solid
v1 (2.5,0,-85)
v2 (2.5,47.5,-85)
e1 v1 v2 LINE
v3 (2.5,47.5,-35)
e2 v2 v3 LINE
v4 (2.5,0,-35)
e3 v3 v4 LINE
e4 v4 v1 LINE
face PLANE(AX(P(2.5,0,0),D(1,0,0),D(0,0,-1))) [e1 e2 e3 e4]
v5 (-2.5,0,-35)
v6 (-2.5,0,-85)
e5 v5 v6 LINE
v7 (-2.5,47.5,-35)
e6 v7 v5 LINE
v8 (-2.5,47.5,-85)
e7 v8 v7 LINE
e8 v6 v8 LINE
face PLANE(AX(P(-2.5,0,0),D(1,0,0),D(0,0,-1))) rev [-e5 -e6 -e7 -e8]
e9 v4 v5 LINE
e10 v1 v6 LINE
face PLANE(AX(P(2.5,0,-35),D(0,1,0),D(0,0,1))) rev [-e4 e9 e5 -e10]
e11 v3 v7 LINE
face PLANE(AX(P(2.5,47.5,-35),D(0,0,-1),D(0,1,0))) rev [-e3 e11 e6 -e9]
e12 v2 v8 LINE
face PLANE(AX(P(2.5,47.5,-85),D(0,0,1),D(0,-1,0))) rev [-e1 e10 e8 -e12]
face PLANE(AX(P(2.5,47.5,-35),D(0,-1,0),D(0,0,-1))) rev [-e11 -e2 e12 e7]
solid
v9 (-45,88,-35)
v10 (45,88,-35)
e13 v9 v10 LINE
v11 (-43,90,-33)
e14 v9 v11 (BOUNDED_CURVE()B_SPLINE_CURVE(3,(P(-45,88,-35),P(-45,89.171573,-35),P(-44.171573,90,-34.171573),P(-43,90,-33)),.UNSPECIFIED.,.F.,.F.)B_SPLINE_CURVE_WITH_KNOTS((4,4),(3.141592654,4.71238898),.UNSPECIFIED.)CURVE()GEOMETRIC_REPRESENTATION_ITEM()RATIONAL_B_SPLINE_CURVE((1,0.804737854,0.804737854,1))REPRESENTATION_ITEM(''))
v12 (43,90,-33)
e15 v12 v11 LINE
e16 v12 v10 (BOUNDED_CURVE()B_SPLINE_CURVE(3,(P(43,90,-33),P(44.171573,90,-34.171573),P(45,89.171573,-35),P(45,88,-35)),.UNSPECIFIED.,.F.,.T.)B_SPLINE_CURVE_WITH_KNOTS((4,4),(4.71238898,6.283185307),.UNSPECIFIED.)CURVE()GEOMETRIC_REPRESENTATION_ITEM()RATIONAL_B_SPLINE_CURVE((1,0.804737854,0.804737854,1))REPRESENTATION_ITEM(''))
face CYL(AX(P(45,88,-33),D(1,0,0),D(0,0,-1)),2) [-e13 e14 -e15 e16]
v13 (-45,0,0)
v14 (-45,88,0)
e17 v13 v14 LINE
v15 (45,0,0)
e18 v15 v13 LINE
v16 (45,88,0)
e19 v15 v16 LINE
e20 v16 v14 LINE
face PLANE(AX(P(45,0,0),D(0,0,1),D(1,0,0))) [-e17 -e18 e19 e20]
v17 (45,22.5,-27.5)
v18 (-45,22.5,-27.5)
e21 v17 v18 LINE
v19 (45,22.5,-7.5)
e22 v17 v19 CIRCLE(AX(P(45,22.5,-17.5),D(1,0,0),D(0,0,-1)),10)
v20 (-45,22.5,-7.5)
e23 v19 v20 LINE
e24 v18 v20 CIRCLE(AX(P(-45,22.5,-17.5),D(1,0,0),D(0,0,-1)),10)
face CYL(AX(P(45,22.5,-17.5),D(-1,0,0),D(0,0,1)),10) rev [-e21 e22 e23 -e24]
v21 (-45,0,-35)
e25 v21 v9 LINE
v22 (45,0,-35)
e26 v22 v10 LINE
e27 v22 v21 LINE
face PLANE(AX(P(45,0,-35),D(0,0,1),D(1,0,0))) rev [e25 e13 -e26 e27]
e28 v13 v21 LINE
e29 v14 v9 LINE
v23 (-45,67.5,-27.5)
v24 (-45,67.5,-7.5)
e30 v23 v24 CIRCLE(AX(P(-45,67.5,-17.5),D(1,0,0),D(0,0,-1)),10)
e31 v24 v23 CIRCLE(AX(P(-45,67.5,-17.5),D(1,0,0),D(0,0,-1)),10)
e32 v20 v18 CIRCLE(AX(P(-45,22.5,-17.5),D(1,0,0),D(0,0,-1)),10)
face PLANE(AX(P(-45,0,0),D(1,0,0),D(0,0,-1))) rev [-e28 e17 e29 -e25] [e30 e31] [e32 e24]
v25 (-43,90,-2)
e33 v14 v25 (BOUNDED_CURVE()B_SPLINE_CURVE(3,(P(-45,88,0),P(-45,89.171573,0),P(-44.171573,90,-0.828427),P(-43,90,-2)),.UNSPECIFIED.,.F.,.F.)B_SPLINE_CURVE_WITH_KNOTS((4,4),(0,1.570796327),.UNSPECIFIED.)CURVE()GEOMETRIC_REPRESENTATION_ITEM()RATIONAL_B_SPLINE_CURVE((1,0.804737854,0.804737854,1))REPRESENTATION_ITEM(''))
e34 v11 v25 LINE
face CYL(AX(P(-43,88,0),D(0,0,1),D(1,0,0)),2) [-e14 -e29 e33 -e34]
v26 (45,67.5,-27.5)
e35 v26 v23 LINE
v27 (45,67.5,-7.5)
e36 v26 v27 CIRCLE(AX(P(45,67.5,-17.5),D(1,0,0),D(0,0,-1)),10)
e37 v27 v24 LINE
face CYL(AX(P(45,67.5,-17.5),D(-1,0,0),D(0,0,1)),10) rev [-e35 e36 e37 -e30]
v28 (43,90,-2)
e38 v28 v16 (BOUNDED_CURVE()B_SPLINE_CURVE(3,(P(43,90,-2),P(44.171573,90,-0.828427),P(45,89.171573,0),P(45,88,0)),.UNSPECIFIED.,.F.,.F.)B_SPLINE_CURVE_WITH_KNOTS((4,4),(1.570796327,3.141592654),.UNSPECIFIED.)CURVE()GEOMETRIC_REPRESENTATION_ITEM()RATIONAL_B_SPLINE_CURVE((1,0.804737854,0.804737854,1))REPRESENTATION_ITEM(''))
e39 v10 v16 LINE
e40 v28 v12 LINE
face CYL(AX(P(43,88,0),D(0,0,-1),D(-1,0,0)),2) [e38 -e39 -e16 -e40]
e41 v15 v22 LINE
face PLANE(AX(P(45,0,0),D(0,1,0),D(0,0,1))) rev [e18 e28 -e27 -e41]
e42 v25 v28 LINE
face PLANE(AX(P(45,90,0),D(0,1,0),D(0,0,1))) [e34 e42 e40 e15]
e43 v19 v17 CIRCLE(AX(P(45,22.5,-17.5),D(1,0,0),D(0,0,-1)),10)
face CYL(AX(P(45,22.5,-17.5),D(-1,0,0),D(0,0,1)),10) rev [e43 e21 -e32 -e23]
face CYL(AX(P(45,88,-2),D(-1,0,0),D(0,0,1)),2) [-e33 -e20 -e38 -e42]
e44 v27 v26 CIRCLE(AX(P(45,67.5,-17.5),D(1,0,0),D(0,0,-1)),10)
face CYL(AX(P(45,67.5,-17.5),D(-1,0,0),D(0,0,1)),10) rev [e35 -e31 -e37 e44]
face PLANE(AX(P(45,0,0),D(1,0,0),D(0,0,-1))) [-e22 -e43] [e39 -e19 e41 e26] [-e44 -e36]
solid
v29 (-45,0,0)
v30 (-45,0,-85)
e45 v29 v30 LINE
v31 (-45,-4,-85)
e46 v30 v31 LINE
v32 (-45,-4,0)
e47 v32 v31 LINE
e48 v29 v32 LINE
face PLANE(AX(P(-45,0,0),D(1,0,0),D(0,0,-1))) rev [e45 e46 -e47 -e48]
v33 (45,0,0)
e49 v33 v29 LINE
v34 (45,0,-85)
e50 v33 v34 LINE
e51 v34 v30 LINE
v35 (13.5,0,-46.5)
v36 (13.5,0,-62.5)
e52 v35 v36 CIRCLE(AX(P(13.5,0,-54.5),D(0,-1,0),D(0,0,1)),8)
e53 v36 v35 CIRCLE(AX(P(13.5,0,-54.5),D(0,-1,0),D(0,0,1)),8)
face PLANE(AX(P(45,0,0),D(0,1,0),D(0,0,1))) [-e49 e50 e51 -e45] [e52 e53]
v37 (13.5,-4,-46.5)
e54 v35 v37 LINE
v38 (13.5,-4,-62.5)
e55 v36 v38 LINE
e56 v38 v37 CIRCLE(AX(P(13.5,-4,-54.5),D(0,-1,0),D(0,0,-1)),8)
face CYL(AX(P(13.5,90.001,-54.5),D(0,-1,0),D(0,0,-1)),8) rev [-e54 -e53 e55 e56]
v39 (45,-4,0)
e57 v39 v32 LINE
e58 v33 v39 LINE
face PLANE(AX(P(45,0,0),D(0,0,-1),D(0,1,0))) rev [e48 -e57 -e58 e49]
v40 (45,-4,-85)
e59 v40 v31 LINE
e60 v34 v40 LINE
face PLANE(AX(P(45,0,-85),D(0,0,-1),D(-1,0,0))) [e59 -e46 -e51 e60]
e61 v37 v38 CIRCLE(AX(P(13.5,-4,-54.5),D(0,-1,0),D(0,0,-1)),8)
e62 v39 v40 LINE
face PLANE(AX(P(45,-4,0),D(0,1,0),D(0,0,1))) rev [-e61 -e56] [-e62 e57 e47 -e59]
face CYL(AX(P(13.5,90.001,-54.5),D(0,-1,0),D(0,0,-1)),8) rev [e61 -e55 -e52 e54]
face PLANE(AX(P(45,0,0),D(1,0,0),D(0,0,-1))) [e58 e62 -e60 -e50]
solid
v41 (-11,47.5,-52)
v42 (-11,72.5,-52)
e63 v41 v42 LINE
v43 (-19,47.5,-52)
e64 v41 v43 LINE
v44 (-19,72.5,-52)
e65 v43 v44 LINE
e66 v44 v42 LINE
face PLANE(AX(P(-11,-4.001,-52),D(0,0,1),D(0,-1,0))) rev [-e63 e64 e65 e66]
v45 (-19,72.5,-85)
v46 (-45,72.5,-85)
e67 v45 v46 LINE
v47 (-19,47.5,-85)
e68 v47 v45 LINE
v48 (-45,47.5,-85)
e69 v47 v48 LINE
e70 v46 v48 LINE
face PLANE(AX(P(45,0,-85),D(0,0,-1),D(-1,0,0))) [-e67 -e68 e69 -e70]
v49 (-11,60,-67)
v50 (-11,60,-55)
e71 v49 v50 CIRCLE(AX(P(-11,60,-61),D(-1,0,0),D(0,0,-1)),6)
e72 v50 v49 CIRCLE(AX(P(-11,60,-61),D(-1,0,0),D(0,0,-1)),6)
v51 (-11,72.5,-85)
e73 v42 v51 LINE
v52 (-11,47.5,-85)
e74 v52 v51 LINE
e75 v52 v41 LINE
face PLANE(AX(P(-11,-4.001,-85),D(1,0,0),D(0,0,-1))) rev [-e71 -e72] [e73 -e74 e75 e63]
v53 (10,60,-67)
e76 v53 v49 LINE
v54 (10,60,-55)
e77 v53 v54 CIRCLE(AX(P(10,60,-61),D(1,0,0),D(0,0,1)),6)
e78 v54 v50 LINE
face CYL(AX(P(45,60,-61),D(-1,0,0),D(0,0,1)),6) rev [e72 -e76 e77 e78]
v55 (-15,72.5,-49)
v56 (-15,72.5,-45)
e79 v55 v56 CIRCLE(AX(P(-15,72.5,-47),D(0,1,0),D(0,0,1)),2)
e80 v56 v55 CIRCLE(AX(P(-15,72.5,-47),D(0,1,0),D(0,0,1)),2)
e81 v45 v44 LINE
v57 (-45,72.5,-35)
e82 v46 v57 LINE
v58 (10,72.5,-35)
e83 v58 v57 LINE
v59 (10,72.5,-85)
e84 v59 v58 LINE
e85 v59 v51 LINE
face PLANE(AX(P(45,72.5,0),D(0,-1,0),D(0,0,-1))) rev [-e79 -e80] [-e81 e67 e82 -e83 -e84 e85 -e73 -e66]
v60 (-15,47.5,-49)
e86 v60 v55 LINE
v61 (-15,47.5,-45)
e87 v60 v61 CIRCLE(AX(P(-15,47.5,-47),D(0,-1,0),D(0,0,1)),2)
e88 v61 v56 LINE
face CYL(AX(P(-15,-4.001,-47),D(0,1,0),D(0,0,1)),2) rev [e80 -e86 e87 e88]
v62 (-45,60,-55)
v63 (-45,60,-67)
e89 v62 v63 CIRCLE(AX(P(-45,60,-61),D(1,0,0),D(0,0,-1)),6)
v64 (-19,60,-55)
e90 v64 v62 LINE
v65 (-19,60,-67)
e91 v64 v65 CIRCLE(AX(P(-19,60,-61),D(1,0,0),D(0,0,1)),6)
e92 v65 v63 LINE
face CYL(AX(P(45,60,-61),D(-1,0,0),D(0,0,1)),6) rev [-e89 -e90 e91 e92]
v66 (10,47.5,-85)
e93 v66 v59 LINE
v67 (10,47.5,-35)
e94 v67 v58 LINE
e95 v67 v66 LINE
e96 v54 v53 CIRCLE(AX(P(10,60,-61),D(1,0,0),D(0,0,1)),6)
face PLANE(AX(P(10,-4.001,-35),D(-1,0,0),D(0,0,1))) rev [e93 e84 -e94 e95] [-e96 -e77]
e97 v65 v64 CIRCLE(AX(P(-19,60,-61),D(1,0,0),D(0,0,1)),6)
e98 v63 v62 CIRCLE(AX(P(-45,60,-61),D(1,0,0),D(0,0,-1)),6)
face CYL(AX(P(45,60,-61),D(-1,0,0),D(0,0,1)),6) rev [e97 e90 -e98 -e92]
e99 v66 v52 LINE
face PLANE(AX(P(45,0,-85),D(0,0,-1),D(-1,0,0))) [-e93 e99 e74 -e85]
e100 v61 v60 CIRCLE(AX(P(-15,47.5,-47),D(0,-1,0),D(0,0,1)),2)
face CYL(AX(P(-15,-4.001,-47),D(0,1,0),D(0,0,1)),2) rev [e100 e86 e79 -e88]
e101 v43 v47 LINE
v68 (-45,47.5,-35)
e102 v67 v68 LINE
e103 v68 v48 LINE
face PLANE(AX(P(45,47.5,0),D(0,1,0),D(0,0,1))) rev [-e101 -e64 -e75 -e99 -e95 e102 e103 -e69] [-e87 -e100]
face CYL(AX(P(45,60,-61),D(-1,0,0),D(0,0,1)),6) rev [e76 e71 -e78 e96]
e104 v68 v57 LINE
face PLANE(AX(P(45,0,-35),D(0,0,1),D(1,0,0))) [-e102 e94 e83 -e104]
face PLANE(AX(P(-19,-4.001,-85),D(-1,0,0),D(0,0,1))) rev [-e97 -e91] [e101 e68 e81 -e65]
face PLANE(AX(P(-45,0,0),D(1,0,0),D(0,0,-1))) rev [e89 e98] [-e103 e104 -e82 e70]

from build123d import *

# Parameters (mm, degrees)
SKETCH1_R           = 10
BOSS_EXTRUDE1_DEPTH = 45
SKETCH1_3_W         = 50
SKETCH1_3_H         = 25
SKETCH1_3_R         = 6
BOSS_EXTRUDE3_DEPTH = 45
BOSS_EXTRUDE4_DEPTH = 45
SKETCH2_R           = 2
SKETCH2_W           = 35
SKETCH2_H           = 50
SKETCH2_W_2         = 8
SKETCH2_H_2         = 33
CUT_EXTRUDE1_DEPTH  = 25
SKETCH3_W           = 50
SKETCH3_H           = 47.5
BOSS_EXTRUDE2_DEPTH = 2.5
FILLET1_R           = 2
SKETCH4_R           = 8
CUT_EXTRUDE2_DEPTH  = 4


with BuildPart() as part:
    # Sketch1 → Boss-Extrude1 (new, symmetric)
    with BuildSketch(Plane(origin=(0, 0, 0), x_dir=(0, 0, -1), z_dir=(1, 0, 0))):
        Polygon((0, 90), (0, 0), (35, 0), (35, 47.5), (35, 72.5), (35, 90), align=None)
        with Locations(Location((17.5, 22.5, 0), (0, 0, 180))):
            Circle(SKETCH1_R, mode=Mode.SUBTRACT)
        with Locations(Location((17.5, 67.5, 0), (0, 0, 180))):
            Circle(SKETCH1_R, mode=Mode.SUBTRACT)
    extrude(amount=BOSS_EXTRUDE1_DEPTH, both=True)

    # Fillet1
    fillet1_edges = [part.edges().sort_by_distance(p)[0] for p in [
        (0, 90, 0),
        (0, 90, -35),
        (45, 90, -17.5),
        (-45, 90, -17.5),
    ]]
    fillet(fillet1_edges, radius=FILLET1_R)


with BuildPart() as body_2:
    # Sketch1<3> → Boss-Extrude3 (new, symmetric)
    with BuildSketch(Plane(origin=(0, 0, 0), x_dir=(0, 0, -1), z_dir=(1, 0, 0))):
        with Locations((60, 60)):
            Rectangle(SKETCH1_3_W, SKETCH1_3_H)
        with Locations(Location((61, 60, 0), (0, 0, 180))):
            Circle(SKETCH1_3_R, mode=Mode.SUBTRACT)
    extrude(amount=BOSS_EXTRUDE3_DEPTH, both=True)

    # Sketch2 → Cut-Extrude1 (cut)
    with BuildSketch(Plane(origin=(0, 72.5, 0), x_dir=(1, 0, 0), z_dir=(0, 1, 0))):
        with Locations(Location((-15, 47, 0), (0, 0, 270))):
            Circle(SKETCH2_R)
        with Locations((27.5, 60)):
            Rectangle(SKETCH2_W, SKETCH2_H)
        with Locations((-15, 68.5)):
            Rectangle(SKETCH2_W_2, SKETCH2_H_2)
    extrude(amount=-CUT_EXTRUDE1_DEPTH, mode=Mode.SUBTRACT)


with BuildPart() as body_3:
    # Sketch1<4> → Boss-Extrude4 (new, symmetric)
    with BuildSketch(Plane(origin=(0, 0, 0), x_dir=(0, 0, -1), z_dir=(1, 0, 0))):
        Polygon((85, 0), (85, -4), (0, -4), (0, 0), (35, 0), align=None)
    extrude(amount=BOSS_EXTRUDE4_DEPTH, both=True)

    # Sketch4 → Cut-Extrude2 (cut)
    with BuildSketch(Plane.XZ.offset(4)):
        with Locations(Location((13.5, -54.5, 0), (0, 0, 270))):
            Circle(SKETCH4_R)
    extrude(amount=-CUT_EXTRUDE2_DEPTH, mode=Mode.SUBTRACT)


with BuildPart() as body_4:
    # Sketch3 → Boss-Extrude2 (new, symmetric)
    with BuildSketch(Plane(origin=(0, 0, 0), x_dir=(0, 0, -1), z_dir=(1, 0, 0))):
        with Locations((60, 23.75)):
            Rectangle(SKETCH3_W, SKETCH3_H)
    extrude(amount=BOSS_EXTRUDE2_DEPTH, both=True)


solid = Compound([part.part, body_2.part, body_3.part, body_4.part])
